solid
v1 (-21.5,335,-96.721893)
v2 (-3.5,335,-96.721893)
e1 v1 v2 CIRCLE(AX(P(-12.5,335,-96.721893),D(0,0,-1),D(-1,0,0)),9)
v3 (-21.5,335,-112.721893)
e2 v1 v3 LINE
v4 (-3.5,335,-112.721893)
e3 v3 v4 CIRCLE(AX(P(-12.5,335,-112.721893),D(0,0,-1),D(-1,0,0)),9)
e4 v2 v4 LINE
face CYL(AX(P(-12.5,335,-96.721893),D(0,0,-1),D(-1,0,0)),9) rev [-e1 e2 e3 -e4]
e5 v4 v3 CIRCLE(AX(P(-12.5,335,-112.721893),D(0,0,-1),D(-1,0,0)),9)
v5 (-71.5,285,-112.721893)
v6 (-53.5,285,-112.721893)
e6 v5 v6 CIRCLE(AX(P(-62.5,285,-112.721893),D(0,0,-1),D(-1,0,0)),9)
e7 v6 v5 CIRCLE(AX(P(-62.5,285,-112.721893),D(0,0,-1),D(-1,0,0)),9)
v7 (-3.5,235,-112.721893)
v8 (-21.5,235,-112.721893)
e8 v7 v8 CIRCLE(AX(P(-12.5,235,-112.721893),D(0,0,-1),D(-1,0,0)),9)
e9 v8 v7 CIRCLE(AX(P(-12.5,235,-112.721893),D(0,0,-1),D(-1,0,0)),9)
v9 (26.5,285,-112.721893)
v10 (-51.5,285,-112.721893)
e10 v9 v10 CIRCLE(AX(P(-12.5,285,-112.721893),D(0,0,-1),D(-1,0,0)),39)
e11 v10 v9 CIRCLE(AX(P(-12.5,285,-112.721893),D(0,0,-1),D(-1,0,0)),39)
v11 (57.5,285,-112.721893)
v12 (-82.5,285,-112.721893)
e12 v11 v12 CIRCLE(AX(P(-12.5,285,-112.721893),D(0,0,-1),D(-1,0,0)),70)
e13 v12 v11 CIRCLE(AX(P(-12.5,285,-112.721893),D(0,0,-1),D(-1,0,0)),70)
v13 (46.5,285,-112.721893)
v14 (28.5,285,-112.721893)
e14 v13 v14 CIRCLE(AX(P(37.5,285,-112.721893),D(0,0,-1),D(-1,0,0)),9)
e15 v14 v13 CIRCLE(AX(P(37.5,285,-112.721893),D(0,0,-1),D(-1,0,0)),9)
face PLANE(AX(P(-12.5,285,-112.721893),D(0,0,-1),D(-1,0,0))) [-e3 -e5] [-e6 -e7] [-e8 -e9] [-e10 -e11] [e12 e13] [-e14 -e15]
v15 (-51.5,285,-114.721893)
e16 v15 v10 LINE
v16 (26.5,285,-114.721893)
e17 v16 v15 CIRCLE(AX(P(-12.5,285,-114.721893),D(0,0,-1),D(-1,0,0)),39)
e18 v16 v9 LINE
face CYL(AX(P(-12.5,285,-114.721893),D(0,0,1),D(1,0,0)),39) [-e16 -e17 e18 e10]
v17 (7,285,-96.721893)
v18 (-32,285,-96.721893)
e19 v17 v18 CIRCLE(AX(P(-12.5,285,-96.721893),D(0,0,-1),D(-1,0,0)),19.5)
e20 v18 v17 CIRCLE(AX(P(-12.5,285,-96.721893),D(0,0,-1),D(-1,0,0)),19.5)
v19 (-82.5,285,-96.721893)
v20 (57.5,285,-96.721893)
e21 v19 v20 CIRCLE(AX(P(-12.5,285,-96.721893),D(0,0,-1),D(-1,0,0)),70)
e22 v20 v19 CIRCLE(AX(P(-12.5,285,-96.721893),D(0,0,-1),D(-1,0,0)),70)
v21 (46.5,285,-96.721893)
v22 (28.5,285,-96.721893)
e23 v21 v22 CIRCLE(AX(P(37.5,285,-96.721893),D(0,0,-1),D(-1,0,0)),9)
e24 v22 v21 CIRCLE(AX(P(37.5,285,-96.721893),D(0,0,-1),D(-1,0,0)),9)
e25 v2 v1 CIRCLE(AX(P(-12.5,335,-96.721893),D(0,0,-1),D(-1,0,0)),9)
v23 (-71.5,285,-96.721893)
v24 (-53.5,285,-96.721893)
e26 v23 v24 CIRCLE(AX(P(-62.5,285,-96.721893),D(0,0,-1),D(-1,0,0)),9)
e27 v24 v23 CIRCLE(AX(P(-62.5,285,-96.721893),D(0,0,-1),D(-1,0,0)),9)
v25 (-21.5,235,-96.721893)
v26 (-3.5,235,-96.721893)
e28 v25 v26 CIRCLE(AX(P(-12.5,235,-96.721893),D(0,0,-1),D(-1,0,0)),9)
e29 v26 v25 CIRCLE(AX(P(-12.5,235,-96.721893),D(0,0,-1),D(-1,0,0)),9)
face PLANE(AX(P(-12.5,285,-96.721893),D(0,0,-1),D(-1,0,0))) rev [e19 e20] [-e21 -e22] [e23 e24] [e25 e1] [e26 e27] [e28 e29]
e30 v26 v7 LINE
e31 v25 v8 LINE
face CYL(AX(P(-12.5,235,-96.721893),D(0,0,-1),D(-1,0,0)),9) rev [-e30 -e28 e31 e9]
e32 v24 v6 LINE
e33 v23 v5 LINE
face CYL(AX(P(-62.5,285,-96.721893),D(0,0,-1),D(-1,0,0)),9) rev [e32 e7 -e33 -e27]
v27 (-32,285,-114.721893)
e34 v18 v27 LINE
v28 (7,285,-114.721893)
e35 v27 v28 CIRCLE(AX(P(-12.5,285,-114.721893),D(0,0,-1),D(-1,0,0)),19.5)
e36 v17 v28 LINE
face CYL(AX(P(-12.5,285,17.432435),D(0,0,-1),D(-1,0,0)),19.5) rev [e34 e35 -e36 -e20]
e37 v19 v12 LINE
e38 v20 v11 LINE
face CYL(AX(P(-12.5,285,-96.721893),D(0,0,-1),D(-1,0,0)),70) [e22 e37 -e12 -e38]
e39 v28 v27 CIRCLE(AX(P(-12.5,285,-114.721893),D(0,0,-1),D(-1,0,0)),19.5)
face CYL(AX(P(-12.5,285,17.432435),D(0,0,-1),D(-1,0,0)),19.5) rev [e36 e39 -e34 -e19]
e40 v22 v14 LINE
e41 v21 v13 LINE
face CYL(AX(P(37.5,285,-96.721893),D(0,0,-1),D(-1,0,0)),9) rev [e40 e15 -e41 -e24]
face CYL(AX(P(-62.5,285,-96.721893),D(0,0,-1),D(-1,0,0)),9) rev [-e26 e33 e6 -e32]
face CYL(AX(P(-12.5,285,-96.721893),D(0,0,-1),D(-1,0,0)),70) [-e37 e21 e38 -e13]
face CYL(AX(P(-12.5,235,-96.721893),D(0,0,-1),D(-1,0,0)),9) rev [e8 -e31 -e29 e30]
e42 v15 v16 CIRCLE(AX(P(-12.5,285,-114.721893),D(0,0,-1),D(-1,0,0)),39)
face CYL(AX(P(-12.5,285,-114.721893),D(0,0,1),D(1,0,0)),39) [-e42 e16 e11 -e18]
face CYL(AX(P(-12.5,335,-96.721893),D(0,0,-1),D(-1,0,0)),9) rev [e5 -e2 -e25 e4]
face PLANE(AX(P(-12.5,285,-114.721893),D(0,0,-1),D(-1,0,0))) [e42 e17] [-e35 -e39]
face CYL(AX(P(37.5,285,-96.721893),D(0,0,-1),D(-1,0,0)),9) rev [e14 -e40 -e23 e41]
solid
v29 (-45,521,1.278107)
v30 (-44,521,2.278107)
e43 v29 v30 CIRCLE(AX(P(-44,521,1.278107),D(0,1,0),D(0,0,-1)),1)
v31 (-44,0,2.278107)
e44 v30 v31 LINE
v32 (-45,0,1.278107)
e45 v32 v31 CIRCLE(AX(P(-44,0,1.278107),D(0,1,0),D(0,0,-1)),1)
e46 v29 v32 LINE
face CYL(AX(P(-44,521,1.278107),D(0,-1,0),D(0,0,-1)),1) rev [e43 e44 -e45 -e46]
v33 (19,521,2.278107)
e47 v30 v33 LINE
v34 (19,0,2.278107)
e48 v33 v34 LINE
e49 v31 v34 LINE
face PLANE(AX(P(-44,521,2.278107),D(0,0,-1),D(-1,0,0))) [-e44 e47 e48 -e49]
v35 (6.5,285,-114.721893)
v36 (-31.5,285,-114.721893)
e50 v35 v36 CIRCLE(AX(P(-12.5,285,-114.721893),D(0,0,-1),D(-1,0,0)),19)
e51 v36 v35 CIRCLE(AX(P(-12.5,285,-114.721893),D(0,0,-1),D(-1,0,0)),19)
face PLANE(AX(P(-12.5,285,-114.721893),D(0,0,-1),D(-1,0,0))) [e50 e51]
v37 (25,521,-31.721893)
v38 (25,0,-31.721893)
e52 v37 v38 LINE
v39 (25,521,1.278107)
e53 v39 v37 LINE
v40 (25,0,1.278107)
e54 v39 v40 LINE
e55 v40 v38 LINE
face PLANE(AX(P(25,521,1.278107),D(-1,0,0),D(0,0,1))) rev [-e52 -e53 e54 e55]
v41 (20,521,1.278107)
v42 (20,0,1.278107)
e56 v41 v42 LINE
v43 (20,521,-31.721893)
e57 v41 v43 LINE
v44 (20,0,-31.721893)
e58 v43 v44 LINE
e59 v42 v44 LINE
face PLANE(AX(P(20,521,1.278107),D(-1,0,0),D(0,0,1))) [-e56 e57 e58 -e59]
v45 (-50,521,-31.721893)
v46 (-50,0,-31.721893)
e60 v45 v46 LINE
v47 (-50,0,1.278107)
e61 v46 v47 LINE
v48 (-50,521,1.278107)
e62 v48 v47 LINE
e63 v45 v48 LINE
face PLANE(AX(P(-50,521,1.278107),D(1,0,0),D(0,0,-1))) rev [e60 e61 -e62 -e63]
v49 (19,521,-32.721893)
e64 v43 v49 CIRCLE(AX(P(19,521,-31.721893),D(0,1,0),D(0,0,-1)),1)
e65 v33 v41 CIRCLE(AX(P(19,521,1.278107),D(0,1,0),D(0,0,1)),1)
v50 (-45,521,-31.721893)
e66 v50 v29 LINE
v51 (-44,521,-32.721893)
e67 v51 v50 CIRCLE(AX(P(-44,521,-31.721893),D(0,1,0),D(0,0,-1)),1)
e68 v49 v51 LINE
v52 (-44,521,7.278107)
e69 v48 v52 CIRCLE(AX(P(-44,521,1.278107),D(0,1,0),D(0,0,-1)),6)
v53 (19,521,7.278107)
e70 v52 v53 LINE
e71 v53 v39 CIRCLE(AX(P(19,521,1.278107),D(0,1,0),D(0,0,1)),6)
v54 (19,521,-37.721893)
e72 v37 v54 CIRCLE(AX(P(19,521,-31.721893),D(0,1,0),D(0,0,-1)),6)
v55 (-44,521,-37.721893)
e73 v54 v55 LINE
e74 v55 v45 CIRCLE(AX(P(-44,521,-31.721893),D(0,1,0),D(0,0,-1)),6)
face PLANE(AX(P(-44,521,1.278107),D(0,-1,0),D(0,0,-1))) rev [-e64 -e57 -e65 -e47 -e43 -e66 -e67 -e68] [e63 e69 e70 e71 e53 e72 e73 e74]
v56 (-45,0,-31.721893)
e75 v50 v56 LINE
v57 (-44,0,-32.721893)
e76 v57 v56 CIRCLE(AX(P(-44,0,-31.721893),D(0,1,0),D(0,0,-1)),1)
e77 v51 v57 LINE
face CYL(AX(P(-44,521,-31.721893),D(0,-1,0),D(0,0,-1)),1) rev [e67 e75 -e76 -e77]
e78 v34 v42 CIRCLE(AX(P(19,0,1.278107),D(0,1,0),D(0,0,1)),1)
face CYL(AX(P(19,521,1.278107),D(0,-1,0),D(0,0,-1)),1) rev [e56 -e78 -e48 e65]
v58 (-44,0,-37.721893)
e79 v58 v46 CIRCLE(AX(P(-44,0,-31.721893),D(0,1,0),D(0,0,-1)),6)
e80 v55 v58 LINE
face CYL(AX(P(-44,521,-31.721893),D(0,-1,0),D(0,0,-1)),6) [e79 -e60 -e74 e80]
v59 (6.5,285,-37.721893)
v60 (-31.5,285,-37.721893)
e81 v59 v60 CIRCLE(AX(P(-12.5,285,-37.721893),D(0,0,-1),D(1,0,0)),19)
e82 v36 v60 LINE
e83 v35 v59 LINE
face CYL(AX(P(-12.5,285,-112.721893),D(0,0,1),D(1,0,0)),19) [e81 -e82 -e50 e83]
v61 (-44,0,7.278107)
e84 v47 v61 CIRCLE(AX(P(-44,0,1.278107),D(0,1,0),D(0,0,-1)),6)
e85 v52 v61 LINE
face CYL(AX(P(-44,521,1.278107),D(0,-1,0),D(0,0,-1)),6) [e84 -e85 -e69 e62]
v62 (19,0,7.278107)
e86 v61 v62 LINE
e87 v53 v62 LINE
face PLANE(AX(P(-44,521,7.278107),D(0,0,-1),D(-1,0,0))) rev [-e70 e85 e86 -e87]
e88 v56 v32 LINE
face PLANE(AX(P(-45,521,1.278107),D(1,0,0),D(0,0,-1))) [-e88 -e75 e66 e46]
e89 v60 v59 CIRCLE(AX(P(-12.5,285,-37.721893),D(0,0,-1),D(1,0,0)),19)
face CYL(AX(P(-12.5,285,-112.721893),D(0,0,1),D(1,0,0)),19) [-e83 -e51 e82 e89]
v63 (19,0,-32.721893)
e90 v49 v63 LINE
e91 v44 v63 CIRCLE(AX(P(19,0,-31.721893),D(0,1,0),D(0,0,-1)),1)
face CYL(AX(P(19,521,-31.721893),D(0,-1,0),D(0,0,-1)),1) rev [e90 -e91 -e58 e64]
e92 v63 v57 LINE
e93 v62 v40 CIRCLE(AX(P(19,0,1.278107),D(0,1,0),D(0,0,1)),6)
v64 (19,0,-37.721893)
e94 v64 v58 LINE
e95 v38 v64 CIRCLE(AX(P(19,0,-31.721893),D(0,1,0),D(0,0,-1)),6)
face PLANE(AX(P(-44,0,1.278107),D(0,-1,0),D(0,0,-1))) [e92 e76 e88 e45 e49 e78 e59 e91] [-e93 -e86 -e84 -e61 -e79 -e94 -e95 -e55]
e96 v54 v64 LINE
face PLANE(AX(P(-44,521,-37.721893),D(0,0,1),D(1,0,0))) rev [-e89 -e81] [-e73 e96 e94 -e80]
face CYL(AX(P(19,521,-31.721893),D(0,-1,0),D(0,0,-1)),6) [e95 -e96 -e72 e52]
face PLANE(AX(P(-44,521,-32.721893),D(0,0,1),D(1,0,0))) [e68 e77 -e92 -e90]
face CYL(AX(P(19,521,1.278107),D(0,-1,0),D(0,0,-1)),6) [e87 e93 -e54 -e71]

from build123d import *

# Parameters (mm, degrees)
EXTRUDE_1_DEPTH     = 521
SKETCH_2_R          = 19
EXTRUDE_2_DEPTH     = 75
SKETCH_3_R          = 70
SKETCH_3_R_2        = 9
EXTRUDE_3_DEPTH     = 16
SKETCH_4_R          = 39
EXTRUDE_4_DEPTH     = 2
CUT_EXTRUDE_START   = -77
SKETCH_5_R          = 19.5
SKETCH_5_R_2        = 19
CUT_EXTRUDE_1_DEPTH = 77


with BuildPart() as part:
    # 草图1 → 凸台-拉伸1 (new body)
    with BuildSketch(Plane(origin=(0, 0, 0), x_dir=(1, 0, 0), z_dir=(0, 1, 0))):
        with BuildLine():
            Line((-44, -7.278106509), (19, -7.278106509))
            ThreePointArc((19, -7.278106509), (23.242640687, -5.520747196), (25, -1.278106509))
            Line((25, -1.278106509), (25, 31.721893491))
            ThreePointArc((25, 31.721893491), (23.242640687, 35.964534178), (19, 37.721893491))
            Line((19, 37.721893491), (-44, 37.721893491))
            ThreePointArc((-44, 37.721893491), (-48.242640687, 35.964534178), (-50, 31.721893491))
            Line((-50, 31.721893491), (-50, -1.278106509))
            ThreePointArc((-50, -1.278106509), (-48.242640687, -5.520747196), (-44, -7.278106509))
        make_face()
        with BuildLine():
            Line((-44, -2.278106509), (19, -2.278106509))
            ThreePointArc((19, -2.278106509), (19.707106781, -1.98521329), (20, -1.278106509))
            Line((20, -1.278106509), (20, 31.721893491))
            ThreePointArc((20, 31.721893491), (19.707106781, 32.429000272), (19, 32.721893491))
            Line((19, 32.721893491), (-44, 32.721893491))
            ThreePointArc((-44, 32.721893491), (-44.707106781, 32.429000272), (-45, 31.721893491))
            Line((-45, 31.721893491), (-45, -1.278106509))
            ThreePointArc((-45, -1.278106509), (-44.707106781, -1.98521329), (-44, -2.278106509))
        make_face(mode=Mode.SUBTRACT)
    extrude(amount=EXTRUDE_1_DEPTH)

    # 草图2 → 凸台-拉伸2 (add)
    with BuildSketch(Plane(origin=(0, 0, -37.721893491), x_dir=(-1, 0, 0), z_dir=(0, 0, -1))):
        with Locations(Location((12.5, 285, 0), (0, 0, 180))):
            Circle(SKETCH_2_R)
    extrude(amount=EXTRUDE_2_DEPTH)

    # 草图3 → 凸台-拉伸3 (add)
    with BuildSketch(Plane(origin=(0, 0, -112.721893491), x_dir=(-1, 0, 0), z_dir=(0, 0, -1))):
        with Locations((12.5, 285)):
            Circle(SKETCH_3_R)
        with Locations((12.5, 335)):
            Circle(SKETCH_3_R_2, mode=Mode.SUBTRACT)
        with Locations((62.5, 285)):
            Circle(SKETCH_3_R_2, mode=Mode.SUBTRACT)
        with Locations((12.5, 235)):
            Circle(SKETCH_3_R_2, mode=Mode.SUBTRACT)
        with Locations((-37.5, 285)):
            Circle(SKETCH_3_R_2, mode=Mode.SUBTRACT)
    extrude(amount=-EXTRUDE_3_DEPTH)

    # 草图4 → 凸台-拉伸4 (add)
    with BuildSketch(Plane(origin=(0, 0, -112.721893491), x_dir=(-1, 0, 0), z_dir=(0, 0, -1))):
        with Locations((12.5, 285)):
            Circle(SKETCH_4_R)
    extrude(amount=EXTRUDE_4_DEPTH)

    # 草图5 → 切除-拉伸1 (cut)
    with BuildSketch(Plane(origin=(0, 0, -114.721893491), x_dir=(-1, 0, 0), z_dir=(0, 0, -1)).offset(CUT_EXTRUDE_START)):
        with Locations((12.5, 285)):
            Circle(SKETCH_5_R)
        with Locations(Location((12.5, 285, 0), (0, 0, 180))):
            Circle(SKETCH_5_R_2, mode=Mode.SUBTRACT)
    extrude(amount=CUT_EXTRUDE_1_DEPTH, mode=Mode.SUBTRACT)


with BuildPart() as cut_extrude_1_piece_1:
    # of the separate pieces the step leaves, piece 1, a body of its own (cut_extrude_1_pieces)
    add(part.part.solids().sort_by_distance((-44, 0, 7.278106509))[0])


with BuildPart() as cut_extrude_1_piece_2:
    # of the separate pieces the step leaves, piece 2, a body of its own (cut_extrude_1_pieces)
    add(part.part.solids().sort_by_distance((-82.5, 285, -96.721893491))[0])


solid = Compound([cut_extrude_1_piece_1.part, cut_extrude_1_piece_2.part])
